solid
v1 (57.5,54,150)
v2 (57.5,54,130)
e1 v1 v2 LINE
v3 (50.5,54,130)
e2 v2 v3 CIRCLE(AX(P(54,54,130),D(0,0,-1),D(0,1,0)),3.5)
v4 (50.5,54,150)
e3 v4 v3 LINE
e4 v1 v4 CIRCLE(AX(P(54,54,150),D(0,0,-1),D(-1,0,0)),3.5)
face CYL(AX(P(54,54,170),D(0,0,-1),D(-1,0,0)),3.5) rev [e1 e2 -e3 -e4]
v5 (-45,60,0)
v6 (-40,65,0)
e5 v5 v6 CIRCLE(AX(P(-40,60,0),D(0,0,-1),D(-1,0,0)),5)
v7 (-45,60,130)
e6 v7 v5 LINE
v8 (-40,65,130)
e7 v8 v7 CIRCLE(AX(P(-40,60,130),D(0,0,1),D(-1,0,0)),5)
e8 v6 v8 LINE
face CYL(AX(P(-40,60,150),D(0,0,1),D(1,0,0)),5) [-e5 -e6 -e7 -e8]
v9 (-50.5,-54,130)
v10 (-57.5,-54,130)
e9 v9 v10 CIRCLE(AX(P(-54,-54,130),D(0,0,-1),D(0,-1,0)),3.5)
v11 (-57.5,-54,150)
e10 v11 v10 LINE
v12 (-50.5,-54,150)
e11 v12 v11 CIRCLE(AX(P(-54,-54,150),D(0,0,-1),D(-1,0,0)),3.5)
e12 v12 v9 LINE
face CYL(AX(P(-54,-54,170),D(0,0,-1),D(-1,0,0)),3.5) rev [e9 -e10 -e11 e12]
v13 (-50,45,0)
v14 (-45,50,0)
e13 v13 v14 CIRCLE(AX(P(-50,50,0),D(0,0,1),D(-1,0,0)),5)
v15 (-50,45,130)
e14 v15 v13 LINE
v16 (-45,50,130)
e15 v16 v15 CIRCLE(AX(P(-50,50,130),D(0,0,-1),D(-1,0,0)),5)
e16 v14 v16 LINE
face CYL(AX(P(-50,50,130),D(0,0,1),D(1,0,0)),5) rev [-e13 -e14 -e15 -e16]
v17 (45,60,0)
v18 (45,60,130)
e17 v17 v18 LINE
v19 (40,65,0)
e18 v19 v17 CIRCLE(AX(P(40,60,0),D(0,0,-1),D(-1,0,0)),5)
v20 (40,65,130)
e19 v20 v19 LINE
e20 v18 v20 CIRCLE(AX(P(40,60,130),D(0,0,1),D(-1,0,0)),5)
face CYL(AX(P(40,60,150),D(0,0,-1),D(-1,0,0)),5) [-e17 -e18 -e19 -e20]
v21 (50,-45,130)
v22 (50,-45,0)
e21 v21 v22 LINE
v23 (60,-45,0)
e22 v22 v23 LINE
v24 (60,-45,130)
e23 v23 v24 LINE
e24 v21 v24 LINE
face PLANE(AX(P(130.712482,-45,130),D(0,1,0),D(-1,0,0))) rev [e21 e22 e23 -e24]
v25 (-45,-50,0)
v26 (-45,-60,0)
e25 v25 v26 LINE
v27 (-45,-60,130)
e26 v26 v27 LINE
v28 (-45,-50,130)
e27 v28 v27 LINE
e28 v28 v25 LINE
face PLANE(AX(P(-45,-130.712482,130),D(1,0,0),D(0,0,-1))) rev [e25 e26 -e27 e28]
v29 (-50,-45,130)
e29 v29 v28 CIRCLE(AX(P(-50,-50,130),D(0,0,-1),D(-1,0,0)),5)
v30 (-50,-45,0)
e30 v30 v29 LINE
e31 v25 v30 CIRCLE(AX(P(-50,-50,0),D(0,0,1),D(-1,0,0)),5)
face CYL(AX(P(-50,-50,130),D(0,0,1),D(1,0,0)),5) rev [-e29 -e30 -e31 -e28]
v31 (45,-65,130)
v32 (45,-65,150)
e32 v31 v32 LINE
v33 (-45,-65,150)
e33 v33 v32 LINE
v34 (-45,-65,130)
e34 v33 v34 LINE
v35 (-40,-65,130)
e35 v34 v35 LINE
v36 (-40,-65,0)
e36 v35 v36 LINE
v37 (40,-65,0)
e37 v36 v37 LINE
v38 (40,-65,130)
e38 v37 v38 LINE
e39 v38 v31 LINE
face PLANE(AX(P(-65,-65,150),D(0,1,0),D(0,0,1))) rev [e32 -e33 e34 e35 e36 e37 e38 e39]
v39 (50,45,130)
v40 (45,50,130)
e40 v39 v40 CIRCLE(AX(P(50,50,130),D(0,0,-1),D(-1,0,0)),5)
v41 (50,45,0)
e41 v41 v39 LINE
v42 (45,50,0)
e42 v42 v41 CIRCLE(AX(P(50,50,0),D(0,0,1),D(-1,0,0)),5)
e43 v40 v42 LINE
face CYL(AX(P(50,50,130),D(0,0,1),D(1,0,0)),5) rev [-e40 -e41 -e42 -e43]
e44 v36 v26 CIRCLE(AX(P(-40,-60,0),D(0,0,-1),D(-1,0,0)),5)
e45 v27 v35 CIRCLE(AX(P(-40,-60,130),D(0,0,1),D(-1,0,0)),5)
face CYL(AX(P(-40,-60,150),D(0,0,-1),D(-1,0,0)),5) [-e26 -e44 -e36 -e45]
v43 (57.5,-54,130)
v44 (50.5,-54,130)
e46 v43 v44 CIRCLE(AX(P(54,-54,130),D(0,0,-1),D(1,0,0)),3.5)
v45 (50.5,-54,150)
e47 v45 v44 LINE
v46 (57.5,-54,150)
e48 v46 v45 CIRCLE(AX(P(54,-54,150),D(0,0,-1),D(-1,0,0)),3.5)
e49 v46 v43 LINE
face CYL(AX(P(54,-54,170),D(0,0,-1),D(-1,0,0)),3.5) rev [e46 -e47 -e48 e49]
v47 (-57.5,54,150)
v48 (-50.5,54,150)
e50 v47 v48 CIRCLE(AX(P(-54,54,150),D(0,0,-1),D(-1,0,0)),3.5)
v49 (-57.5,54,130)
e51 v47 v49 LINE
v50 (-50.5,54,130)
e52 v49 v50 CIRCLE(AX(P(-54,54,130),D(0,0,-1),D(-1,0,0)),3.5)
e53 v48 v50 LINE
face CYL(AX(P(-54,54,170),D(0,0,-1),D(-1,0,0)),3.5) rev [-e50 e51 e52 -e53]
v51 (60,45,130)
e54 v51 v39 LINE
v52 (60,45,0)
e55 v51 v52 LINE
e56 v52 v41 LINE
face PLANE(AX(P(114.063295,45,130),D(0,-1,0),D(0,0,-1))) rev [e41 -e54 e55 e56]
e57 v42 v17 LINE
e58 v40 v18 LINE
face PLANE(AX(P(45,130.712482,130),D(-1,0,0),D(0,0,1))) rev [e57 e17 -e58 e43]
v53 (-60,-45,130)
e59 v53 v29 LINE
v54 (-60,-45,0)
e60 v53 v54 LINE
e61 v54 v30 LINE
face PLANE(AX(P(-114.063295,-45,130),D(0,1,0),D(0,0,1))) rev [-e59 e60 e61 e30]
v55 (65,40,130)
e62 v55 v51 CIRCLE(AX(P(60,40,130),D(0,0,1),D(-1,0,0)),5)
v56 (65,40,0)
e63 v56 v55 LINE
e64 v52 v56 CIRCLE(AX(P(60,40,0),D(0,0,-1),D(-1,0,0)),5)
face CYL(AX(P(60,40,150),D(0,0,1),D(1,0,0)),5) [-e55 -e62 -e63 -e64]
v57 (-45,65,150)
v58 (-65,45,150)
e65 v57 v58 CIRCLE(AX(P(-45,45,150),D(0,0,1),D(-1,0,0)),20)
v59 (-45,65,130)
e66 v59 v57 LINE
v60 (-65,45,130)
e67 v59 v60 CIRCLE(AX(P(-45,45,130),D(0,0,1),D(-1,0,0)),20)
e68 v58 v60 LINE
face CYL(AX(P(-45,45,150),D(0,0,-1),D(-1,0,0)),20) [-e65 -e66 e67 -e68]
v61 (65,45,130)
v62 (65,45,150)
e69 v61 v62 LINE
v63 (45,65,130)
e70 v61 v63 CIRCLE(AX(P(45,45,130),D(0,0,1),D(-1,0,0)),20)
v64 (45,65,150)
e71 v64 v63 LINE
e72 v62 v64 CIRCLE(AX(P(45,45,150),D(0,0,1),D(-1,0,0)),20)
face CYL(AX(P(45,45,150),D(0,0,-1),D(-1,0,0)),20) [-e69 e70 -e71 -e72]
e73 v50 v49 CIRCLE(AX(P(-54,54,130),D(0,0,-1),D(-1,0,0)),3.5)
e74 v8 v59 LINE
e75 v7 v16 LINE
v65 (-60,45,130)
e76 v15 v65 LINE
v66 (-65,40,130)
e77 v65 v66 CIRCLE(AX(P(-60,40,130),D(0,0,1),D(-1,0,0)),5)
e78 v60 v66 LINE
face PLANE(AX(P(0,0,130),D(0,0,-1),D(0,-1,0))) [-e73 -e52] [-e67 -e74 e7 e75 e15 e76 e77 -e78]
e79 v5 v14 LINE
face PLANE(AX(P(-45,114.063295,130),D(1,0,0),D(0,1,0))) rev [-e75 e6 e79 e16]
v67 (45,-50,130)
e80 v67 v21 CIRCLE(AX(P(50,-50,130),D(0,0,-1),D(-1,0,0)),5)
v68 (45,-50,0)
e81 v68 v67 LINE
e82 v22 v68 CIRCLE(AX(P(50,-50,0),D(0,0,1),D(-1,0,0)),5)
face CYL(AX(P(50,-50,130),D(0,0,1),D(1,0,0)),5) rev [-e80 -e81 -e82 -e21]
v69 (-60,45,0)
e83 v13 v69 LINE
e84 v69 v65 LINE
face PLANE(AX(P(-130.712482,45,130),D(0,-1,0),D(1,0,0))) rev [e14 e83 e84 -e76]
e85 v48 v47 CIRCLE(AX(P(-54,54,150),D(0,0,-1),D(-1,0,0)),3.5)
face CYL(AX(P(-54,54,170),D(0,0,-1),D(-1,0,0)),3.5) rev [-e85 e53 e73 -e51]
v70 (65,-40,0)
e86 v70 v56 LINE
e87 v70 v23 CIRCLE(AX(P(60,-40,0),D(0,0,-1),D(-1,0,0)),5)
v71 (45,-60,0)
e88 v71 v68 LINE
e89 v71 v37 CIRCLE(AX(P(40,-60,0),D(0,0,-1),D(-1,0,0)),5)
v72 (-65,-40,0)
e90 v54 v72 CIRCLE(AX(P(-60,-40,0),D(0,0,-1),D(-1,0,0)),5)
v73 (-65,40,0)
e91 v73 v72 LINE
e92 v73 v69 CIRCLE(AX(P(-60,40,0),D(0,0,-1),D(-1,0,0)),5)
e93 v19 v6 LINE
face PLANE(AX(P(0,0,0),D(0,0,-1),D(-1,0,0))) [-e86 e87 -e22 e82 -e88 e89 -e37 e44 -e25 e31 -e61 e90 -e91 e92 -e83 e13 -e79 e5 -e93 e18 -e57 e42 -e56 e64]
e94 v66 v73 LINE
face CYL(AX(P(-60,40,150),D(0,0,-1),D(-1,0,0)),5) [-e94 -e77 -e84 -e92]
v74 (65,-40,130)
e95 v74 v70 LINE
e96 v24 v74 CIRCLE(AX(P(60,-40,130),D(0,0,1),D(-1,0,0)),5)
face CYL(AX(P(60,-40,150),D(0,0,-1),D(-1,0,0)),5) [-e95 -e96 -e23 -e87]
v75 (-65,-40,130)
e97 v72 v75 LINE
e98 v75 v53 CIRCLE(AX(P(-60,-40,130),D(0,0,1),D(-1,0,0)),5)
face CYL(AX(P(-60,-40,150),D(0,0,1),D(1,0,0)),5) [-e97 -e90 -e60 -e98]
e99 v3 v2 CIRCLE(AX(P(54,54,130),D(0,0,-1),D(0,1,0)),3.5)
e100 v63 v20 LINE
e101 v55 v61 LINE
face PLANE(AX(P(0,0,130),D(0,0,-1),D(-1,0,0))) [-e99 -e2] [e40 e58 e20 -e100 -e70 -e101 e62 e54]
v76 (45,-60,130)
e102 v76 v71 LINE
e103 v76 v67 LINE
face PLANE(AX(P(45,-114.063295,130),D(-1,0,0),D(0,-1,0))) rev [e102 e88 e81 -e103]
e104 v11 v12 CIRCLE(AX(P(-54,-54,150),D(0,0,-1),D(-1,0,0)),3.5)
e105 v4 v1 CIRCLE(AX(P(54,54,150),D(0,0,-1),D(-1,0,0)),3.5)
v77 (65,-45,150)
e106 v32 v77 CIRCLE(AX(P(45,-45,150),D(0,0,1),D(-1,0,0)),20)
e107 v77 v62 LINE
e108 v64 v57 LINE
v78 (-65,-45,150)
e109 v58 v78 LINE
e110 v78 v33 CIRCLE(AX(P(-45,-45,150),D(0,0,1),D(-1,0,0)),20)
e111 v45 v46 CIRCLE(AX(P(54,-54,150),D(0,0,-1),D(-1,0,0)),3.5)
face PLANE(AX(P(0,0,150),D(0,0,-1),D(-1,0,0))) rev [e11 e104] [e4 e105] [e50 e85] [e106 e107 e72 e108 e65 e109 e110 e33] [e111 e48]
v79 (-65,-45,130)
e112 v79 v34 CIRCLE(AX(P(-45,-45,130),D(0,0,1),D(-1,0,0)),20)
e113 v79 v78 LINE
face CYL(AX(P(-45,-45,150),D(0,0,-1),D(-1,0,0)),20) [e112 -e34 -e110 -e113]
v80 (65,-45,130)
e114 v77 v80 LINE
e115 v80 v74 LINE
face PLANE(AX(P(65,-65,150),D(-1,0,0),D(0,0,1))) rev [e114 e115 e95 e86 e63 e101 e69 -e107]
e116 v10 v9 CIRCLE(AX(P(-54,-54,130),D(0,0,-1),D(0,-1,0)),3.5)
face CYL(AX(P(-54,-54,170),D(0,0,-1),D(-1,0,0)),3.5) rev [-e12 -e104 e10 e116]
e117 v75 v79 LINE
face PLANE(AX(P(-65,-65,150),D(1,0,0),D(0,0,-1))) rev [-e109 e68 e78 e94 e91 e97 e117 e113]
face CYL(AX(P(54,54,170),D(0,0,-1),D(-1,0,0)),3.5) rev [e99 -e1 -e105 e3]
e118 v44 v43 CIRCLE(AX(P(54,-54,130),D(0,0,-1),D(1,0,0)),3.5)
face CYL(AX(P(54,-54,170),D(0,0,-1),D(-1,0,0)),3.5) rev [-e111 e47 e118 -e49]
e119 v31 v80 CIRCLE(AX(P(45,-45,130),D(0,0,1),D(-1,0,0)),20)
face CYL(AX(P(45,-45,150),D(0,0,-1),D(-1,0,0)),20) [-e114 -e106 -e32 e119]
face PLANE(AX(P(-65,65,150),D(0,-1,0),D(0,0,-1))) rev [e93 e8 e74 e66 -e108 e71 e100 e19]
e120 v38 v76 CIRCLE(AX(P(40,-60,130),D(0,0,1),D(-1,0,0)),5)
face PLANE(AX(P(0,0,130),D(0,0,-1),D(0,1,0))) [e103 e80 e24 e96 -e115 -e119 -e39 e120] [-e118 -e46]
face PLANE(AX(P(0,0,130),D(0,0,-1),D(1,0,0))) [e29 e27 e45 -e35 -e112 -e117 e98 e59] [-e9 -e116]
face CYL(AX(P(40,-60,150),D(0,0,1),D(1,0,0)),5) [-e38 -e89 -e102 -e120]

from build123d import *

# Parameters (mm, degrees)
SKETCH1_W           = 130
SKETCH1_H           = 130
BOSS_EXTRUDE1_DEPTH = 150
FILLET1_R           = 20
SKETCH2_W           = 69.063294878
SKETCH2_H           = 85.712482036
CUT_EXTRUDE1_DEPTH  = 130
CIRPATTERN1_COUNT   = 4
FILLET2_R           = 5
FILLET3_R           = 5
SKETCH4_R           = 3.5
CUT_EXTRUDE2_DEPTH  = 40
CIRPATTERN2_COUNT   = 4


with BuildPart() as part:
    # Sketch1 → Boss-Extrude1 (new body)
    with BuildSketch(Plane.XY):
        Rectangle(SKETCH1_W, SKETCH1_H)
    extrude(amount=BOSS_EXTRUDE1_DEPTH)

    # Fillet1
    fillet1_edges = [part.edges().sort_by_distance(p)[0] for p in [
        (65, -65, 75),
        (-65, -65, 75),
        (-65, 65, 75),
        (65, 65, 75),
    ]]
    fillet(fillet1_edges, radius=FILLET1_R)

    # Sketch2 → Cut-Extrude1 (cut)
    with BuildSketch(Plane(origin=(0, 0, 0), x_dir=(-1, 0, 0), z_dir=(0, 0, -1))):
        with Locations((-79.531647439, 87.856241018)):
            Rectangle(SKETCH2_W, SKETCH2_H)
    cut_extrude1 = extrude(amount=-CUT_EXTRUDE1_DEPTH, mode=Mode.SUBTRACT)

    # CirPattern1: Cut-Extrude1 ×4 about axis
    cirpattern1_axis = Axis((0, 0, 0), (0, 0, 1))
    for i in range(1, CIRPATTERN1_COUNT):
        add(cut_extrude1.rotate(cirpattern1_axis, i * 360 / CIRPATTERN1_COUNT), mode=Mode.SUBTRACT)

    # Fillet2
    fillet2_edges = [part.edges().sort_by_distance(p)[0] for p in [
        (45, 45, 65),
        (-45, 45, 65),
        (-45, -45, 65),
        (45, -45, 65),
    ]]
    fillet(fillet2_edges, radius=FILLET2_R)

    # Fillet3
    fillet3_edges = [part.edges().sort_by_distance(p)[0] for p in [
        (45, -65, 65),
        (-65, -45, 65),
        (65, 45, 65),
        (-45, 65, 65),
        (45, 65, 65),
        (-65, 45, 65),
        (65, -45, 65),
        (-45, -65, 65),
    ]]
    fillet(fillet3_edges, radius=FILLET3_R)

    # Sketch4 → Cut-Extrude2 (cut)
    with BuildSketch(Plane(origin=(0, 0, 130), x_dir=(-1, 0, 0), z_dir=(0, 0, -1))):
        with Locations((54, 54)):
            Circle(SKETCH4_R)
    cut_extrude2 = extrude(amount=-CUT_EXTRUDE2_DEPTH, mode=Mode.SUBTRACT)

    # CirPattern2: Cut-Extrude2 ×4 about axis
    cirpattern2_axis = Axis((0, 0, 0), (0, 0, 1))
    for i in range(1, CIRPATTERN2_COUNT):
        add(cut_extrude2.rotate(cirpattern2_axis, i * 360 / CIRPATTERN2_COUNT), mode=Mode.SUBTRACT)


solid = part.part
